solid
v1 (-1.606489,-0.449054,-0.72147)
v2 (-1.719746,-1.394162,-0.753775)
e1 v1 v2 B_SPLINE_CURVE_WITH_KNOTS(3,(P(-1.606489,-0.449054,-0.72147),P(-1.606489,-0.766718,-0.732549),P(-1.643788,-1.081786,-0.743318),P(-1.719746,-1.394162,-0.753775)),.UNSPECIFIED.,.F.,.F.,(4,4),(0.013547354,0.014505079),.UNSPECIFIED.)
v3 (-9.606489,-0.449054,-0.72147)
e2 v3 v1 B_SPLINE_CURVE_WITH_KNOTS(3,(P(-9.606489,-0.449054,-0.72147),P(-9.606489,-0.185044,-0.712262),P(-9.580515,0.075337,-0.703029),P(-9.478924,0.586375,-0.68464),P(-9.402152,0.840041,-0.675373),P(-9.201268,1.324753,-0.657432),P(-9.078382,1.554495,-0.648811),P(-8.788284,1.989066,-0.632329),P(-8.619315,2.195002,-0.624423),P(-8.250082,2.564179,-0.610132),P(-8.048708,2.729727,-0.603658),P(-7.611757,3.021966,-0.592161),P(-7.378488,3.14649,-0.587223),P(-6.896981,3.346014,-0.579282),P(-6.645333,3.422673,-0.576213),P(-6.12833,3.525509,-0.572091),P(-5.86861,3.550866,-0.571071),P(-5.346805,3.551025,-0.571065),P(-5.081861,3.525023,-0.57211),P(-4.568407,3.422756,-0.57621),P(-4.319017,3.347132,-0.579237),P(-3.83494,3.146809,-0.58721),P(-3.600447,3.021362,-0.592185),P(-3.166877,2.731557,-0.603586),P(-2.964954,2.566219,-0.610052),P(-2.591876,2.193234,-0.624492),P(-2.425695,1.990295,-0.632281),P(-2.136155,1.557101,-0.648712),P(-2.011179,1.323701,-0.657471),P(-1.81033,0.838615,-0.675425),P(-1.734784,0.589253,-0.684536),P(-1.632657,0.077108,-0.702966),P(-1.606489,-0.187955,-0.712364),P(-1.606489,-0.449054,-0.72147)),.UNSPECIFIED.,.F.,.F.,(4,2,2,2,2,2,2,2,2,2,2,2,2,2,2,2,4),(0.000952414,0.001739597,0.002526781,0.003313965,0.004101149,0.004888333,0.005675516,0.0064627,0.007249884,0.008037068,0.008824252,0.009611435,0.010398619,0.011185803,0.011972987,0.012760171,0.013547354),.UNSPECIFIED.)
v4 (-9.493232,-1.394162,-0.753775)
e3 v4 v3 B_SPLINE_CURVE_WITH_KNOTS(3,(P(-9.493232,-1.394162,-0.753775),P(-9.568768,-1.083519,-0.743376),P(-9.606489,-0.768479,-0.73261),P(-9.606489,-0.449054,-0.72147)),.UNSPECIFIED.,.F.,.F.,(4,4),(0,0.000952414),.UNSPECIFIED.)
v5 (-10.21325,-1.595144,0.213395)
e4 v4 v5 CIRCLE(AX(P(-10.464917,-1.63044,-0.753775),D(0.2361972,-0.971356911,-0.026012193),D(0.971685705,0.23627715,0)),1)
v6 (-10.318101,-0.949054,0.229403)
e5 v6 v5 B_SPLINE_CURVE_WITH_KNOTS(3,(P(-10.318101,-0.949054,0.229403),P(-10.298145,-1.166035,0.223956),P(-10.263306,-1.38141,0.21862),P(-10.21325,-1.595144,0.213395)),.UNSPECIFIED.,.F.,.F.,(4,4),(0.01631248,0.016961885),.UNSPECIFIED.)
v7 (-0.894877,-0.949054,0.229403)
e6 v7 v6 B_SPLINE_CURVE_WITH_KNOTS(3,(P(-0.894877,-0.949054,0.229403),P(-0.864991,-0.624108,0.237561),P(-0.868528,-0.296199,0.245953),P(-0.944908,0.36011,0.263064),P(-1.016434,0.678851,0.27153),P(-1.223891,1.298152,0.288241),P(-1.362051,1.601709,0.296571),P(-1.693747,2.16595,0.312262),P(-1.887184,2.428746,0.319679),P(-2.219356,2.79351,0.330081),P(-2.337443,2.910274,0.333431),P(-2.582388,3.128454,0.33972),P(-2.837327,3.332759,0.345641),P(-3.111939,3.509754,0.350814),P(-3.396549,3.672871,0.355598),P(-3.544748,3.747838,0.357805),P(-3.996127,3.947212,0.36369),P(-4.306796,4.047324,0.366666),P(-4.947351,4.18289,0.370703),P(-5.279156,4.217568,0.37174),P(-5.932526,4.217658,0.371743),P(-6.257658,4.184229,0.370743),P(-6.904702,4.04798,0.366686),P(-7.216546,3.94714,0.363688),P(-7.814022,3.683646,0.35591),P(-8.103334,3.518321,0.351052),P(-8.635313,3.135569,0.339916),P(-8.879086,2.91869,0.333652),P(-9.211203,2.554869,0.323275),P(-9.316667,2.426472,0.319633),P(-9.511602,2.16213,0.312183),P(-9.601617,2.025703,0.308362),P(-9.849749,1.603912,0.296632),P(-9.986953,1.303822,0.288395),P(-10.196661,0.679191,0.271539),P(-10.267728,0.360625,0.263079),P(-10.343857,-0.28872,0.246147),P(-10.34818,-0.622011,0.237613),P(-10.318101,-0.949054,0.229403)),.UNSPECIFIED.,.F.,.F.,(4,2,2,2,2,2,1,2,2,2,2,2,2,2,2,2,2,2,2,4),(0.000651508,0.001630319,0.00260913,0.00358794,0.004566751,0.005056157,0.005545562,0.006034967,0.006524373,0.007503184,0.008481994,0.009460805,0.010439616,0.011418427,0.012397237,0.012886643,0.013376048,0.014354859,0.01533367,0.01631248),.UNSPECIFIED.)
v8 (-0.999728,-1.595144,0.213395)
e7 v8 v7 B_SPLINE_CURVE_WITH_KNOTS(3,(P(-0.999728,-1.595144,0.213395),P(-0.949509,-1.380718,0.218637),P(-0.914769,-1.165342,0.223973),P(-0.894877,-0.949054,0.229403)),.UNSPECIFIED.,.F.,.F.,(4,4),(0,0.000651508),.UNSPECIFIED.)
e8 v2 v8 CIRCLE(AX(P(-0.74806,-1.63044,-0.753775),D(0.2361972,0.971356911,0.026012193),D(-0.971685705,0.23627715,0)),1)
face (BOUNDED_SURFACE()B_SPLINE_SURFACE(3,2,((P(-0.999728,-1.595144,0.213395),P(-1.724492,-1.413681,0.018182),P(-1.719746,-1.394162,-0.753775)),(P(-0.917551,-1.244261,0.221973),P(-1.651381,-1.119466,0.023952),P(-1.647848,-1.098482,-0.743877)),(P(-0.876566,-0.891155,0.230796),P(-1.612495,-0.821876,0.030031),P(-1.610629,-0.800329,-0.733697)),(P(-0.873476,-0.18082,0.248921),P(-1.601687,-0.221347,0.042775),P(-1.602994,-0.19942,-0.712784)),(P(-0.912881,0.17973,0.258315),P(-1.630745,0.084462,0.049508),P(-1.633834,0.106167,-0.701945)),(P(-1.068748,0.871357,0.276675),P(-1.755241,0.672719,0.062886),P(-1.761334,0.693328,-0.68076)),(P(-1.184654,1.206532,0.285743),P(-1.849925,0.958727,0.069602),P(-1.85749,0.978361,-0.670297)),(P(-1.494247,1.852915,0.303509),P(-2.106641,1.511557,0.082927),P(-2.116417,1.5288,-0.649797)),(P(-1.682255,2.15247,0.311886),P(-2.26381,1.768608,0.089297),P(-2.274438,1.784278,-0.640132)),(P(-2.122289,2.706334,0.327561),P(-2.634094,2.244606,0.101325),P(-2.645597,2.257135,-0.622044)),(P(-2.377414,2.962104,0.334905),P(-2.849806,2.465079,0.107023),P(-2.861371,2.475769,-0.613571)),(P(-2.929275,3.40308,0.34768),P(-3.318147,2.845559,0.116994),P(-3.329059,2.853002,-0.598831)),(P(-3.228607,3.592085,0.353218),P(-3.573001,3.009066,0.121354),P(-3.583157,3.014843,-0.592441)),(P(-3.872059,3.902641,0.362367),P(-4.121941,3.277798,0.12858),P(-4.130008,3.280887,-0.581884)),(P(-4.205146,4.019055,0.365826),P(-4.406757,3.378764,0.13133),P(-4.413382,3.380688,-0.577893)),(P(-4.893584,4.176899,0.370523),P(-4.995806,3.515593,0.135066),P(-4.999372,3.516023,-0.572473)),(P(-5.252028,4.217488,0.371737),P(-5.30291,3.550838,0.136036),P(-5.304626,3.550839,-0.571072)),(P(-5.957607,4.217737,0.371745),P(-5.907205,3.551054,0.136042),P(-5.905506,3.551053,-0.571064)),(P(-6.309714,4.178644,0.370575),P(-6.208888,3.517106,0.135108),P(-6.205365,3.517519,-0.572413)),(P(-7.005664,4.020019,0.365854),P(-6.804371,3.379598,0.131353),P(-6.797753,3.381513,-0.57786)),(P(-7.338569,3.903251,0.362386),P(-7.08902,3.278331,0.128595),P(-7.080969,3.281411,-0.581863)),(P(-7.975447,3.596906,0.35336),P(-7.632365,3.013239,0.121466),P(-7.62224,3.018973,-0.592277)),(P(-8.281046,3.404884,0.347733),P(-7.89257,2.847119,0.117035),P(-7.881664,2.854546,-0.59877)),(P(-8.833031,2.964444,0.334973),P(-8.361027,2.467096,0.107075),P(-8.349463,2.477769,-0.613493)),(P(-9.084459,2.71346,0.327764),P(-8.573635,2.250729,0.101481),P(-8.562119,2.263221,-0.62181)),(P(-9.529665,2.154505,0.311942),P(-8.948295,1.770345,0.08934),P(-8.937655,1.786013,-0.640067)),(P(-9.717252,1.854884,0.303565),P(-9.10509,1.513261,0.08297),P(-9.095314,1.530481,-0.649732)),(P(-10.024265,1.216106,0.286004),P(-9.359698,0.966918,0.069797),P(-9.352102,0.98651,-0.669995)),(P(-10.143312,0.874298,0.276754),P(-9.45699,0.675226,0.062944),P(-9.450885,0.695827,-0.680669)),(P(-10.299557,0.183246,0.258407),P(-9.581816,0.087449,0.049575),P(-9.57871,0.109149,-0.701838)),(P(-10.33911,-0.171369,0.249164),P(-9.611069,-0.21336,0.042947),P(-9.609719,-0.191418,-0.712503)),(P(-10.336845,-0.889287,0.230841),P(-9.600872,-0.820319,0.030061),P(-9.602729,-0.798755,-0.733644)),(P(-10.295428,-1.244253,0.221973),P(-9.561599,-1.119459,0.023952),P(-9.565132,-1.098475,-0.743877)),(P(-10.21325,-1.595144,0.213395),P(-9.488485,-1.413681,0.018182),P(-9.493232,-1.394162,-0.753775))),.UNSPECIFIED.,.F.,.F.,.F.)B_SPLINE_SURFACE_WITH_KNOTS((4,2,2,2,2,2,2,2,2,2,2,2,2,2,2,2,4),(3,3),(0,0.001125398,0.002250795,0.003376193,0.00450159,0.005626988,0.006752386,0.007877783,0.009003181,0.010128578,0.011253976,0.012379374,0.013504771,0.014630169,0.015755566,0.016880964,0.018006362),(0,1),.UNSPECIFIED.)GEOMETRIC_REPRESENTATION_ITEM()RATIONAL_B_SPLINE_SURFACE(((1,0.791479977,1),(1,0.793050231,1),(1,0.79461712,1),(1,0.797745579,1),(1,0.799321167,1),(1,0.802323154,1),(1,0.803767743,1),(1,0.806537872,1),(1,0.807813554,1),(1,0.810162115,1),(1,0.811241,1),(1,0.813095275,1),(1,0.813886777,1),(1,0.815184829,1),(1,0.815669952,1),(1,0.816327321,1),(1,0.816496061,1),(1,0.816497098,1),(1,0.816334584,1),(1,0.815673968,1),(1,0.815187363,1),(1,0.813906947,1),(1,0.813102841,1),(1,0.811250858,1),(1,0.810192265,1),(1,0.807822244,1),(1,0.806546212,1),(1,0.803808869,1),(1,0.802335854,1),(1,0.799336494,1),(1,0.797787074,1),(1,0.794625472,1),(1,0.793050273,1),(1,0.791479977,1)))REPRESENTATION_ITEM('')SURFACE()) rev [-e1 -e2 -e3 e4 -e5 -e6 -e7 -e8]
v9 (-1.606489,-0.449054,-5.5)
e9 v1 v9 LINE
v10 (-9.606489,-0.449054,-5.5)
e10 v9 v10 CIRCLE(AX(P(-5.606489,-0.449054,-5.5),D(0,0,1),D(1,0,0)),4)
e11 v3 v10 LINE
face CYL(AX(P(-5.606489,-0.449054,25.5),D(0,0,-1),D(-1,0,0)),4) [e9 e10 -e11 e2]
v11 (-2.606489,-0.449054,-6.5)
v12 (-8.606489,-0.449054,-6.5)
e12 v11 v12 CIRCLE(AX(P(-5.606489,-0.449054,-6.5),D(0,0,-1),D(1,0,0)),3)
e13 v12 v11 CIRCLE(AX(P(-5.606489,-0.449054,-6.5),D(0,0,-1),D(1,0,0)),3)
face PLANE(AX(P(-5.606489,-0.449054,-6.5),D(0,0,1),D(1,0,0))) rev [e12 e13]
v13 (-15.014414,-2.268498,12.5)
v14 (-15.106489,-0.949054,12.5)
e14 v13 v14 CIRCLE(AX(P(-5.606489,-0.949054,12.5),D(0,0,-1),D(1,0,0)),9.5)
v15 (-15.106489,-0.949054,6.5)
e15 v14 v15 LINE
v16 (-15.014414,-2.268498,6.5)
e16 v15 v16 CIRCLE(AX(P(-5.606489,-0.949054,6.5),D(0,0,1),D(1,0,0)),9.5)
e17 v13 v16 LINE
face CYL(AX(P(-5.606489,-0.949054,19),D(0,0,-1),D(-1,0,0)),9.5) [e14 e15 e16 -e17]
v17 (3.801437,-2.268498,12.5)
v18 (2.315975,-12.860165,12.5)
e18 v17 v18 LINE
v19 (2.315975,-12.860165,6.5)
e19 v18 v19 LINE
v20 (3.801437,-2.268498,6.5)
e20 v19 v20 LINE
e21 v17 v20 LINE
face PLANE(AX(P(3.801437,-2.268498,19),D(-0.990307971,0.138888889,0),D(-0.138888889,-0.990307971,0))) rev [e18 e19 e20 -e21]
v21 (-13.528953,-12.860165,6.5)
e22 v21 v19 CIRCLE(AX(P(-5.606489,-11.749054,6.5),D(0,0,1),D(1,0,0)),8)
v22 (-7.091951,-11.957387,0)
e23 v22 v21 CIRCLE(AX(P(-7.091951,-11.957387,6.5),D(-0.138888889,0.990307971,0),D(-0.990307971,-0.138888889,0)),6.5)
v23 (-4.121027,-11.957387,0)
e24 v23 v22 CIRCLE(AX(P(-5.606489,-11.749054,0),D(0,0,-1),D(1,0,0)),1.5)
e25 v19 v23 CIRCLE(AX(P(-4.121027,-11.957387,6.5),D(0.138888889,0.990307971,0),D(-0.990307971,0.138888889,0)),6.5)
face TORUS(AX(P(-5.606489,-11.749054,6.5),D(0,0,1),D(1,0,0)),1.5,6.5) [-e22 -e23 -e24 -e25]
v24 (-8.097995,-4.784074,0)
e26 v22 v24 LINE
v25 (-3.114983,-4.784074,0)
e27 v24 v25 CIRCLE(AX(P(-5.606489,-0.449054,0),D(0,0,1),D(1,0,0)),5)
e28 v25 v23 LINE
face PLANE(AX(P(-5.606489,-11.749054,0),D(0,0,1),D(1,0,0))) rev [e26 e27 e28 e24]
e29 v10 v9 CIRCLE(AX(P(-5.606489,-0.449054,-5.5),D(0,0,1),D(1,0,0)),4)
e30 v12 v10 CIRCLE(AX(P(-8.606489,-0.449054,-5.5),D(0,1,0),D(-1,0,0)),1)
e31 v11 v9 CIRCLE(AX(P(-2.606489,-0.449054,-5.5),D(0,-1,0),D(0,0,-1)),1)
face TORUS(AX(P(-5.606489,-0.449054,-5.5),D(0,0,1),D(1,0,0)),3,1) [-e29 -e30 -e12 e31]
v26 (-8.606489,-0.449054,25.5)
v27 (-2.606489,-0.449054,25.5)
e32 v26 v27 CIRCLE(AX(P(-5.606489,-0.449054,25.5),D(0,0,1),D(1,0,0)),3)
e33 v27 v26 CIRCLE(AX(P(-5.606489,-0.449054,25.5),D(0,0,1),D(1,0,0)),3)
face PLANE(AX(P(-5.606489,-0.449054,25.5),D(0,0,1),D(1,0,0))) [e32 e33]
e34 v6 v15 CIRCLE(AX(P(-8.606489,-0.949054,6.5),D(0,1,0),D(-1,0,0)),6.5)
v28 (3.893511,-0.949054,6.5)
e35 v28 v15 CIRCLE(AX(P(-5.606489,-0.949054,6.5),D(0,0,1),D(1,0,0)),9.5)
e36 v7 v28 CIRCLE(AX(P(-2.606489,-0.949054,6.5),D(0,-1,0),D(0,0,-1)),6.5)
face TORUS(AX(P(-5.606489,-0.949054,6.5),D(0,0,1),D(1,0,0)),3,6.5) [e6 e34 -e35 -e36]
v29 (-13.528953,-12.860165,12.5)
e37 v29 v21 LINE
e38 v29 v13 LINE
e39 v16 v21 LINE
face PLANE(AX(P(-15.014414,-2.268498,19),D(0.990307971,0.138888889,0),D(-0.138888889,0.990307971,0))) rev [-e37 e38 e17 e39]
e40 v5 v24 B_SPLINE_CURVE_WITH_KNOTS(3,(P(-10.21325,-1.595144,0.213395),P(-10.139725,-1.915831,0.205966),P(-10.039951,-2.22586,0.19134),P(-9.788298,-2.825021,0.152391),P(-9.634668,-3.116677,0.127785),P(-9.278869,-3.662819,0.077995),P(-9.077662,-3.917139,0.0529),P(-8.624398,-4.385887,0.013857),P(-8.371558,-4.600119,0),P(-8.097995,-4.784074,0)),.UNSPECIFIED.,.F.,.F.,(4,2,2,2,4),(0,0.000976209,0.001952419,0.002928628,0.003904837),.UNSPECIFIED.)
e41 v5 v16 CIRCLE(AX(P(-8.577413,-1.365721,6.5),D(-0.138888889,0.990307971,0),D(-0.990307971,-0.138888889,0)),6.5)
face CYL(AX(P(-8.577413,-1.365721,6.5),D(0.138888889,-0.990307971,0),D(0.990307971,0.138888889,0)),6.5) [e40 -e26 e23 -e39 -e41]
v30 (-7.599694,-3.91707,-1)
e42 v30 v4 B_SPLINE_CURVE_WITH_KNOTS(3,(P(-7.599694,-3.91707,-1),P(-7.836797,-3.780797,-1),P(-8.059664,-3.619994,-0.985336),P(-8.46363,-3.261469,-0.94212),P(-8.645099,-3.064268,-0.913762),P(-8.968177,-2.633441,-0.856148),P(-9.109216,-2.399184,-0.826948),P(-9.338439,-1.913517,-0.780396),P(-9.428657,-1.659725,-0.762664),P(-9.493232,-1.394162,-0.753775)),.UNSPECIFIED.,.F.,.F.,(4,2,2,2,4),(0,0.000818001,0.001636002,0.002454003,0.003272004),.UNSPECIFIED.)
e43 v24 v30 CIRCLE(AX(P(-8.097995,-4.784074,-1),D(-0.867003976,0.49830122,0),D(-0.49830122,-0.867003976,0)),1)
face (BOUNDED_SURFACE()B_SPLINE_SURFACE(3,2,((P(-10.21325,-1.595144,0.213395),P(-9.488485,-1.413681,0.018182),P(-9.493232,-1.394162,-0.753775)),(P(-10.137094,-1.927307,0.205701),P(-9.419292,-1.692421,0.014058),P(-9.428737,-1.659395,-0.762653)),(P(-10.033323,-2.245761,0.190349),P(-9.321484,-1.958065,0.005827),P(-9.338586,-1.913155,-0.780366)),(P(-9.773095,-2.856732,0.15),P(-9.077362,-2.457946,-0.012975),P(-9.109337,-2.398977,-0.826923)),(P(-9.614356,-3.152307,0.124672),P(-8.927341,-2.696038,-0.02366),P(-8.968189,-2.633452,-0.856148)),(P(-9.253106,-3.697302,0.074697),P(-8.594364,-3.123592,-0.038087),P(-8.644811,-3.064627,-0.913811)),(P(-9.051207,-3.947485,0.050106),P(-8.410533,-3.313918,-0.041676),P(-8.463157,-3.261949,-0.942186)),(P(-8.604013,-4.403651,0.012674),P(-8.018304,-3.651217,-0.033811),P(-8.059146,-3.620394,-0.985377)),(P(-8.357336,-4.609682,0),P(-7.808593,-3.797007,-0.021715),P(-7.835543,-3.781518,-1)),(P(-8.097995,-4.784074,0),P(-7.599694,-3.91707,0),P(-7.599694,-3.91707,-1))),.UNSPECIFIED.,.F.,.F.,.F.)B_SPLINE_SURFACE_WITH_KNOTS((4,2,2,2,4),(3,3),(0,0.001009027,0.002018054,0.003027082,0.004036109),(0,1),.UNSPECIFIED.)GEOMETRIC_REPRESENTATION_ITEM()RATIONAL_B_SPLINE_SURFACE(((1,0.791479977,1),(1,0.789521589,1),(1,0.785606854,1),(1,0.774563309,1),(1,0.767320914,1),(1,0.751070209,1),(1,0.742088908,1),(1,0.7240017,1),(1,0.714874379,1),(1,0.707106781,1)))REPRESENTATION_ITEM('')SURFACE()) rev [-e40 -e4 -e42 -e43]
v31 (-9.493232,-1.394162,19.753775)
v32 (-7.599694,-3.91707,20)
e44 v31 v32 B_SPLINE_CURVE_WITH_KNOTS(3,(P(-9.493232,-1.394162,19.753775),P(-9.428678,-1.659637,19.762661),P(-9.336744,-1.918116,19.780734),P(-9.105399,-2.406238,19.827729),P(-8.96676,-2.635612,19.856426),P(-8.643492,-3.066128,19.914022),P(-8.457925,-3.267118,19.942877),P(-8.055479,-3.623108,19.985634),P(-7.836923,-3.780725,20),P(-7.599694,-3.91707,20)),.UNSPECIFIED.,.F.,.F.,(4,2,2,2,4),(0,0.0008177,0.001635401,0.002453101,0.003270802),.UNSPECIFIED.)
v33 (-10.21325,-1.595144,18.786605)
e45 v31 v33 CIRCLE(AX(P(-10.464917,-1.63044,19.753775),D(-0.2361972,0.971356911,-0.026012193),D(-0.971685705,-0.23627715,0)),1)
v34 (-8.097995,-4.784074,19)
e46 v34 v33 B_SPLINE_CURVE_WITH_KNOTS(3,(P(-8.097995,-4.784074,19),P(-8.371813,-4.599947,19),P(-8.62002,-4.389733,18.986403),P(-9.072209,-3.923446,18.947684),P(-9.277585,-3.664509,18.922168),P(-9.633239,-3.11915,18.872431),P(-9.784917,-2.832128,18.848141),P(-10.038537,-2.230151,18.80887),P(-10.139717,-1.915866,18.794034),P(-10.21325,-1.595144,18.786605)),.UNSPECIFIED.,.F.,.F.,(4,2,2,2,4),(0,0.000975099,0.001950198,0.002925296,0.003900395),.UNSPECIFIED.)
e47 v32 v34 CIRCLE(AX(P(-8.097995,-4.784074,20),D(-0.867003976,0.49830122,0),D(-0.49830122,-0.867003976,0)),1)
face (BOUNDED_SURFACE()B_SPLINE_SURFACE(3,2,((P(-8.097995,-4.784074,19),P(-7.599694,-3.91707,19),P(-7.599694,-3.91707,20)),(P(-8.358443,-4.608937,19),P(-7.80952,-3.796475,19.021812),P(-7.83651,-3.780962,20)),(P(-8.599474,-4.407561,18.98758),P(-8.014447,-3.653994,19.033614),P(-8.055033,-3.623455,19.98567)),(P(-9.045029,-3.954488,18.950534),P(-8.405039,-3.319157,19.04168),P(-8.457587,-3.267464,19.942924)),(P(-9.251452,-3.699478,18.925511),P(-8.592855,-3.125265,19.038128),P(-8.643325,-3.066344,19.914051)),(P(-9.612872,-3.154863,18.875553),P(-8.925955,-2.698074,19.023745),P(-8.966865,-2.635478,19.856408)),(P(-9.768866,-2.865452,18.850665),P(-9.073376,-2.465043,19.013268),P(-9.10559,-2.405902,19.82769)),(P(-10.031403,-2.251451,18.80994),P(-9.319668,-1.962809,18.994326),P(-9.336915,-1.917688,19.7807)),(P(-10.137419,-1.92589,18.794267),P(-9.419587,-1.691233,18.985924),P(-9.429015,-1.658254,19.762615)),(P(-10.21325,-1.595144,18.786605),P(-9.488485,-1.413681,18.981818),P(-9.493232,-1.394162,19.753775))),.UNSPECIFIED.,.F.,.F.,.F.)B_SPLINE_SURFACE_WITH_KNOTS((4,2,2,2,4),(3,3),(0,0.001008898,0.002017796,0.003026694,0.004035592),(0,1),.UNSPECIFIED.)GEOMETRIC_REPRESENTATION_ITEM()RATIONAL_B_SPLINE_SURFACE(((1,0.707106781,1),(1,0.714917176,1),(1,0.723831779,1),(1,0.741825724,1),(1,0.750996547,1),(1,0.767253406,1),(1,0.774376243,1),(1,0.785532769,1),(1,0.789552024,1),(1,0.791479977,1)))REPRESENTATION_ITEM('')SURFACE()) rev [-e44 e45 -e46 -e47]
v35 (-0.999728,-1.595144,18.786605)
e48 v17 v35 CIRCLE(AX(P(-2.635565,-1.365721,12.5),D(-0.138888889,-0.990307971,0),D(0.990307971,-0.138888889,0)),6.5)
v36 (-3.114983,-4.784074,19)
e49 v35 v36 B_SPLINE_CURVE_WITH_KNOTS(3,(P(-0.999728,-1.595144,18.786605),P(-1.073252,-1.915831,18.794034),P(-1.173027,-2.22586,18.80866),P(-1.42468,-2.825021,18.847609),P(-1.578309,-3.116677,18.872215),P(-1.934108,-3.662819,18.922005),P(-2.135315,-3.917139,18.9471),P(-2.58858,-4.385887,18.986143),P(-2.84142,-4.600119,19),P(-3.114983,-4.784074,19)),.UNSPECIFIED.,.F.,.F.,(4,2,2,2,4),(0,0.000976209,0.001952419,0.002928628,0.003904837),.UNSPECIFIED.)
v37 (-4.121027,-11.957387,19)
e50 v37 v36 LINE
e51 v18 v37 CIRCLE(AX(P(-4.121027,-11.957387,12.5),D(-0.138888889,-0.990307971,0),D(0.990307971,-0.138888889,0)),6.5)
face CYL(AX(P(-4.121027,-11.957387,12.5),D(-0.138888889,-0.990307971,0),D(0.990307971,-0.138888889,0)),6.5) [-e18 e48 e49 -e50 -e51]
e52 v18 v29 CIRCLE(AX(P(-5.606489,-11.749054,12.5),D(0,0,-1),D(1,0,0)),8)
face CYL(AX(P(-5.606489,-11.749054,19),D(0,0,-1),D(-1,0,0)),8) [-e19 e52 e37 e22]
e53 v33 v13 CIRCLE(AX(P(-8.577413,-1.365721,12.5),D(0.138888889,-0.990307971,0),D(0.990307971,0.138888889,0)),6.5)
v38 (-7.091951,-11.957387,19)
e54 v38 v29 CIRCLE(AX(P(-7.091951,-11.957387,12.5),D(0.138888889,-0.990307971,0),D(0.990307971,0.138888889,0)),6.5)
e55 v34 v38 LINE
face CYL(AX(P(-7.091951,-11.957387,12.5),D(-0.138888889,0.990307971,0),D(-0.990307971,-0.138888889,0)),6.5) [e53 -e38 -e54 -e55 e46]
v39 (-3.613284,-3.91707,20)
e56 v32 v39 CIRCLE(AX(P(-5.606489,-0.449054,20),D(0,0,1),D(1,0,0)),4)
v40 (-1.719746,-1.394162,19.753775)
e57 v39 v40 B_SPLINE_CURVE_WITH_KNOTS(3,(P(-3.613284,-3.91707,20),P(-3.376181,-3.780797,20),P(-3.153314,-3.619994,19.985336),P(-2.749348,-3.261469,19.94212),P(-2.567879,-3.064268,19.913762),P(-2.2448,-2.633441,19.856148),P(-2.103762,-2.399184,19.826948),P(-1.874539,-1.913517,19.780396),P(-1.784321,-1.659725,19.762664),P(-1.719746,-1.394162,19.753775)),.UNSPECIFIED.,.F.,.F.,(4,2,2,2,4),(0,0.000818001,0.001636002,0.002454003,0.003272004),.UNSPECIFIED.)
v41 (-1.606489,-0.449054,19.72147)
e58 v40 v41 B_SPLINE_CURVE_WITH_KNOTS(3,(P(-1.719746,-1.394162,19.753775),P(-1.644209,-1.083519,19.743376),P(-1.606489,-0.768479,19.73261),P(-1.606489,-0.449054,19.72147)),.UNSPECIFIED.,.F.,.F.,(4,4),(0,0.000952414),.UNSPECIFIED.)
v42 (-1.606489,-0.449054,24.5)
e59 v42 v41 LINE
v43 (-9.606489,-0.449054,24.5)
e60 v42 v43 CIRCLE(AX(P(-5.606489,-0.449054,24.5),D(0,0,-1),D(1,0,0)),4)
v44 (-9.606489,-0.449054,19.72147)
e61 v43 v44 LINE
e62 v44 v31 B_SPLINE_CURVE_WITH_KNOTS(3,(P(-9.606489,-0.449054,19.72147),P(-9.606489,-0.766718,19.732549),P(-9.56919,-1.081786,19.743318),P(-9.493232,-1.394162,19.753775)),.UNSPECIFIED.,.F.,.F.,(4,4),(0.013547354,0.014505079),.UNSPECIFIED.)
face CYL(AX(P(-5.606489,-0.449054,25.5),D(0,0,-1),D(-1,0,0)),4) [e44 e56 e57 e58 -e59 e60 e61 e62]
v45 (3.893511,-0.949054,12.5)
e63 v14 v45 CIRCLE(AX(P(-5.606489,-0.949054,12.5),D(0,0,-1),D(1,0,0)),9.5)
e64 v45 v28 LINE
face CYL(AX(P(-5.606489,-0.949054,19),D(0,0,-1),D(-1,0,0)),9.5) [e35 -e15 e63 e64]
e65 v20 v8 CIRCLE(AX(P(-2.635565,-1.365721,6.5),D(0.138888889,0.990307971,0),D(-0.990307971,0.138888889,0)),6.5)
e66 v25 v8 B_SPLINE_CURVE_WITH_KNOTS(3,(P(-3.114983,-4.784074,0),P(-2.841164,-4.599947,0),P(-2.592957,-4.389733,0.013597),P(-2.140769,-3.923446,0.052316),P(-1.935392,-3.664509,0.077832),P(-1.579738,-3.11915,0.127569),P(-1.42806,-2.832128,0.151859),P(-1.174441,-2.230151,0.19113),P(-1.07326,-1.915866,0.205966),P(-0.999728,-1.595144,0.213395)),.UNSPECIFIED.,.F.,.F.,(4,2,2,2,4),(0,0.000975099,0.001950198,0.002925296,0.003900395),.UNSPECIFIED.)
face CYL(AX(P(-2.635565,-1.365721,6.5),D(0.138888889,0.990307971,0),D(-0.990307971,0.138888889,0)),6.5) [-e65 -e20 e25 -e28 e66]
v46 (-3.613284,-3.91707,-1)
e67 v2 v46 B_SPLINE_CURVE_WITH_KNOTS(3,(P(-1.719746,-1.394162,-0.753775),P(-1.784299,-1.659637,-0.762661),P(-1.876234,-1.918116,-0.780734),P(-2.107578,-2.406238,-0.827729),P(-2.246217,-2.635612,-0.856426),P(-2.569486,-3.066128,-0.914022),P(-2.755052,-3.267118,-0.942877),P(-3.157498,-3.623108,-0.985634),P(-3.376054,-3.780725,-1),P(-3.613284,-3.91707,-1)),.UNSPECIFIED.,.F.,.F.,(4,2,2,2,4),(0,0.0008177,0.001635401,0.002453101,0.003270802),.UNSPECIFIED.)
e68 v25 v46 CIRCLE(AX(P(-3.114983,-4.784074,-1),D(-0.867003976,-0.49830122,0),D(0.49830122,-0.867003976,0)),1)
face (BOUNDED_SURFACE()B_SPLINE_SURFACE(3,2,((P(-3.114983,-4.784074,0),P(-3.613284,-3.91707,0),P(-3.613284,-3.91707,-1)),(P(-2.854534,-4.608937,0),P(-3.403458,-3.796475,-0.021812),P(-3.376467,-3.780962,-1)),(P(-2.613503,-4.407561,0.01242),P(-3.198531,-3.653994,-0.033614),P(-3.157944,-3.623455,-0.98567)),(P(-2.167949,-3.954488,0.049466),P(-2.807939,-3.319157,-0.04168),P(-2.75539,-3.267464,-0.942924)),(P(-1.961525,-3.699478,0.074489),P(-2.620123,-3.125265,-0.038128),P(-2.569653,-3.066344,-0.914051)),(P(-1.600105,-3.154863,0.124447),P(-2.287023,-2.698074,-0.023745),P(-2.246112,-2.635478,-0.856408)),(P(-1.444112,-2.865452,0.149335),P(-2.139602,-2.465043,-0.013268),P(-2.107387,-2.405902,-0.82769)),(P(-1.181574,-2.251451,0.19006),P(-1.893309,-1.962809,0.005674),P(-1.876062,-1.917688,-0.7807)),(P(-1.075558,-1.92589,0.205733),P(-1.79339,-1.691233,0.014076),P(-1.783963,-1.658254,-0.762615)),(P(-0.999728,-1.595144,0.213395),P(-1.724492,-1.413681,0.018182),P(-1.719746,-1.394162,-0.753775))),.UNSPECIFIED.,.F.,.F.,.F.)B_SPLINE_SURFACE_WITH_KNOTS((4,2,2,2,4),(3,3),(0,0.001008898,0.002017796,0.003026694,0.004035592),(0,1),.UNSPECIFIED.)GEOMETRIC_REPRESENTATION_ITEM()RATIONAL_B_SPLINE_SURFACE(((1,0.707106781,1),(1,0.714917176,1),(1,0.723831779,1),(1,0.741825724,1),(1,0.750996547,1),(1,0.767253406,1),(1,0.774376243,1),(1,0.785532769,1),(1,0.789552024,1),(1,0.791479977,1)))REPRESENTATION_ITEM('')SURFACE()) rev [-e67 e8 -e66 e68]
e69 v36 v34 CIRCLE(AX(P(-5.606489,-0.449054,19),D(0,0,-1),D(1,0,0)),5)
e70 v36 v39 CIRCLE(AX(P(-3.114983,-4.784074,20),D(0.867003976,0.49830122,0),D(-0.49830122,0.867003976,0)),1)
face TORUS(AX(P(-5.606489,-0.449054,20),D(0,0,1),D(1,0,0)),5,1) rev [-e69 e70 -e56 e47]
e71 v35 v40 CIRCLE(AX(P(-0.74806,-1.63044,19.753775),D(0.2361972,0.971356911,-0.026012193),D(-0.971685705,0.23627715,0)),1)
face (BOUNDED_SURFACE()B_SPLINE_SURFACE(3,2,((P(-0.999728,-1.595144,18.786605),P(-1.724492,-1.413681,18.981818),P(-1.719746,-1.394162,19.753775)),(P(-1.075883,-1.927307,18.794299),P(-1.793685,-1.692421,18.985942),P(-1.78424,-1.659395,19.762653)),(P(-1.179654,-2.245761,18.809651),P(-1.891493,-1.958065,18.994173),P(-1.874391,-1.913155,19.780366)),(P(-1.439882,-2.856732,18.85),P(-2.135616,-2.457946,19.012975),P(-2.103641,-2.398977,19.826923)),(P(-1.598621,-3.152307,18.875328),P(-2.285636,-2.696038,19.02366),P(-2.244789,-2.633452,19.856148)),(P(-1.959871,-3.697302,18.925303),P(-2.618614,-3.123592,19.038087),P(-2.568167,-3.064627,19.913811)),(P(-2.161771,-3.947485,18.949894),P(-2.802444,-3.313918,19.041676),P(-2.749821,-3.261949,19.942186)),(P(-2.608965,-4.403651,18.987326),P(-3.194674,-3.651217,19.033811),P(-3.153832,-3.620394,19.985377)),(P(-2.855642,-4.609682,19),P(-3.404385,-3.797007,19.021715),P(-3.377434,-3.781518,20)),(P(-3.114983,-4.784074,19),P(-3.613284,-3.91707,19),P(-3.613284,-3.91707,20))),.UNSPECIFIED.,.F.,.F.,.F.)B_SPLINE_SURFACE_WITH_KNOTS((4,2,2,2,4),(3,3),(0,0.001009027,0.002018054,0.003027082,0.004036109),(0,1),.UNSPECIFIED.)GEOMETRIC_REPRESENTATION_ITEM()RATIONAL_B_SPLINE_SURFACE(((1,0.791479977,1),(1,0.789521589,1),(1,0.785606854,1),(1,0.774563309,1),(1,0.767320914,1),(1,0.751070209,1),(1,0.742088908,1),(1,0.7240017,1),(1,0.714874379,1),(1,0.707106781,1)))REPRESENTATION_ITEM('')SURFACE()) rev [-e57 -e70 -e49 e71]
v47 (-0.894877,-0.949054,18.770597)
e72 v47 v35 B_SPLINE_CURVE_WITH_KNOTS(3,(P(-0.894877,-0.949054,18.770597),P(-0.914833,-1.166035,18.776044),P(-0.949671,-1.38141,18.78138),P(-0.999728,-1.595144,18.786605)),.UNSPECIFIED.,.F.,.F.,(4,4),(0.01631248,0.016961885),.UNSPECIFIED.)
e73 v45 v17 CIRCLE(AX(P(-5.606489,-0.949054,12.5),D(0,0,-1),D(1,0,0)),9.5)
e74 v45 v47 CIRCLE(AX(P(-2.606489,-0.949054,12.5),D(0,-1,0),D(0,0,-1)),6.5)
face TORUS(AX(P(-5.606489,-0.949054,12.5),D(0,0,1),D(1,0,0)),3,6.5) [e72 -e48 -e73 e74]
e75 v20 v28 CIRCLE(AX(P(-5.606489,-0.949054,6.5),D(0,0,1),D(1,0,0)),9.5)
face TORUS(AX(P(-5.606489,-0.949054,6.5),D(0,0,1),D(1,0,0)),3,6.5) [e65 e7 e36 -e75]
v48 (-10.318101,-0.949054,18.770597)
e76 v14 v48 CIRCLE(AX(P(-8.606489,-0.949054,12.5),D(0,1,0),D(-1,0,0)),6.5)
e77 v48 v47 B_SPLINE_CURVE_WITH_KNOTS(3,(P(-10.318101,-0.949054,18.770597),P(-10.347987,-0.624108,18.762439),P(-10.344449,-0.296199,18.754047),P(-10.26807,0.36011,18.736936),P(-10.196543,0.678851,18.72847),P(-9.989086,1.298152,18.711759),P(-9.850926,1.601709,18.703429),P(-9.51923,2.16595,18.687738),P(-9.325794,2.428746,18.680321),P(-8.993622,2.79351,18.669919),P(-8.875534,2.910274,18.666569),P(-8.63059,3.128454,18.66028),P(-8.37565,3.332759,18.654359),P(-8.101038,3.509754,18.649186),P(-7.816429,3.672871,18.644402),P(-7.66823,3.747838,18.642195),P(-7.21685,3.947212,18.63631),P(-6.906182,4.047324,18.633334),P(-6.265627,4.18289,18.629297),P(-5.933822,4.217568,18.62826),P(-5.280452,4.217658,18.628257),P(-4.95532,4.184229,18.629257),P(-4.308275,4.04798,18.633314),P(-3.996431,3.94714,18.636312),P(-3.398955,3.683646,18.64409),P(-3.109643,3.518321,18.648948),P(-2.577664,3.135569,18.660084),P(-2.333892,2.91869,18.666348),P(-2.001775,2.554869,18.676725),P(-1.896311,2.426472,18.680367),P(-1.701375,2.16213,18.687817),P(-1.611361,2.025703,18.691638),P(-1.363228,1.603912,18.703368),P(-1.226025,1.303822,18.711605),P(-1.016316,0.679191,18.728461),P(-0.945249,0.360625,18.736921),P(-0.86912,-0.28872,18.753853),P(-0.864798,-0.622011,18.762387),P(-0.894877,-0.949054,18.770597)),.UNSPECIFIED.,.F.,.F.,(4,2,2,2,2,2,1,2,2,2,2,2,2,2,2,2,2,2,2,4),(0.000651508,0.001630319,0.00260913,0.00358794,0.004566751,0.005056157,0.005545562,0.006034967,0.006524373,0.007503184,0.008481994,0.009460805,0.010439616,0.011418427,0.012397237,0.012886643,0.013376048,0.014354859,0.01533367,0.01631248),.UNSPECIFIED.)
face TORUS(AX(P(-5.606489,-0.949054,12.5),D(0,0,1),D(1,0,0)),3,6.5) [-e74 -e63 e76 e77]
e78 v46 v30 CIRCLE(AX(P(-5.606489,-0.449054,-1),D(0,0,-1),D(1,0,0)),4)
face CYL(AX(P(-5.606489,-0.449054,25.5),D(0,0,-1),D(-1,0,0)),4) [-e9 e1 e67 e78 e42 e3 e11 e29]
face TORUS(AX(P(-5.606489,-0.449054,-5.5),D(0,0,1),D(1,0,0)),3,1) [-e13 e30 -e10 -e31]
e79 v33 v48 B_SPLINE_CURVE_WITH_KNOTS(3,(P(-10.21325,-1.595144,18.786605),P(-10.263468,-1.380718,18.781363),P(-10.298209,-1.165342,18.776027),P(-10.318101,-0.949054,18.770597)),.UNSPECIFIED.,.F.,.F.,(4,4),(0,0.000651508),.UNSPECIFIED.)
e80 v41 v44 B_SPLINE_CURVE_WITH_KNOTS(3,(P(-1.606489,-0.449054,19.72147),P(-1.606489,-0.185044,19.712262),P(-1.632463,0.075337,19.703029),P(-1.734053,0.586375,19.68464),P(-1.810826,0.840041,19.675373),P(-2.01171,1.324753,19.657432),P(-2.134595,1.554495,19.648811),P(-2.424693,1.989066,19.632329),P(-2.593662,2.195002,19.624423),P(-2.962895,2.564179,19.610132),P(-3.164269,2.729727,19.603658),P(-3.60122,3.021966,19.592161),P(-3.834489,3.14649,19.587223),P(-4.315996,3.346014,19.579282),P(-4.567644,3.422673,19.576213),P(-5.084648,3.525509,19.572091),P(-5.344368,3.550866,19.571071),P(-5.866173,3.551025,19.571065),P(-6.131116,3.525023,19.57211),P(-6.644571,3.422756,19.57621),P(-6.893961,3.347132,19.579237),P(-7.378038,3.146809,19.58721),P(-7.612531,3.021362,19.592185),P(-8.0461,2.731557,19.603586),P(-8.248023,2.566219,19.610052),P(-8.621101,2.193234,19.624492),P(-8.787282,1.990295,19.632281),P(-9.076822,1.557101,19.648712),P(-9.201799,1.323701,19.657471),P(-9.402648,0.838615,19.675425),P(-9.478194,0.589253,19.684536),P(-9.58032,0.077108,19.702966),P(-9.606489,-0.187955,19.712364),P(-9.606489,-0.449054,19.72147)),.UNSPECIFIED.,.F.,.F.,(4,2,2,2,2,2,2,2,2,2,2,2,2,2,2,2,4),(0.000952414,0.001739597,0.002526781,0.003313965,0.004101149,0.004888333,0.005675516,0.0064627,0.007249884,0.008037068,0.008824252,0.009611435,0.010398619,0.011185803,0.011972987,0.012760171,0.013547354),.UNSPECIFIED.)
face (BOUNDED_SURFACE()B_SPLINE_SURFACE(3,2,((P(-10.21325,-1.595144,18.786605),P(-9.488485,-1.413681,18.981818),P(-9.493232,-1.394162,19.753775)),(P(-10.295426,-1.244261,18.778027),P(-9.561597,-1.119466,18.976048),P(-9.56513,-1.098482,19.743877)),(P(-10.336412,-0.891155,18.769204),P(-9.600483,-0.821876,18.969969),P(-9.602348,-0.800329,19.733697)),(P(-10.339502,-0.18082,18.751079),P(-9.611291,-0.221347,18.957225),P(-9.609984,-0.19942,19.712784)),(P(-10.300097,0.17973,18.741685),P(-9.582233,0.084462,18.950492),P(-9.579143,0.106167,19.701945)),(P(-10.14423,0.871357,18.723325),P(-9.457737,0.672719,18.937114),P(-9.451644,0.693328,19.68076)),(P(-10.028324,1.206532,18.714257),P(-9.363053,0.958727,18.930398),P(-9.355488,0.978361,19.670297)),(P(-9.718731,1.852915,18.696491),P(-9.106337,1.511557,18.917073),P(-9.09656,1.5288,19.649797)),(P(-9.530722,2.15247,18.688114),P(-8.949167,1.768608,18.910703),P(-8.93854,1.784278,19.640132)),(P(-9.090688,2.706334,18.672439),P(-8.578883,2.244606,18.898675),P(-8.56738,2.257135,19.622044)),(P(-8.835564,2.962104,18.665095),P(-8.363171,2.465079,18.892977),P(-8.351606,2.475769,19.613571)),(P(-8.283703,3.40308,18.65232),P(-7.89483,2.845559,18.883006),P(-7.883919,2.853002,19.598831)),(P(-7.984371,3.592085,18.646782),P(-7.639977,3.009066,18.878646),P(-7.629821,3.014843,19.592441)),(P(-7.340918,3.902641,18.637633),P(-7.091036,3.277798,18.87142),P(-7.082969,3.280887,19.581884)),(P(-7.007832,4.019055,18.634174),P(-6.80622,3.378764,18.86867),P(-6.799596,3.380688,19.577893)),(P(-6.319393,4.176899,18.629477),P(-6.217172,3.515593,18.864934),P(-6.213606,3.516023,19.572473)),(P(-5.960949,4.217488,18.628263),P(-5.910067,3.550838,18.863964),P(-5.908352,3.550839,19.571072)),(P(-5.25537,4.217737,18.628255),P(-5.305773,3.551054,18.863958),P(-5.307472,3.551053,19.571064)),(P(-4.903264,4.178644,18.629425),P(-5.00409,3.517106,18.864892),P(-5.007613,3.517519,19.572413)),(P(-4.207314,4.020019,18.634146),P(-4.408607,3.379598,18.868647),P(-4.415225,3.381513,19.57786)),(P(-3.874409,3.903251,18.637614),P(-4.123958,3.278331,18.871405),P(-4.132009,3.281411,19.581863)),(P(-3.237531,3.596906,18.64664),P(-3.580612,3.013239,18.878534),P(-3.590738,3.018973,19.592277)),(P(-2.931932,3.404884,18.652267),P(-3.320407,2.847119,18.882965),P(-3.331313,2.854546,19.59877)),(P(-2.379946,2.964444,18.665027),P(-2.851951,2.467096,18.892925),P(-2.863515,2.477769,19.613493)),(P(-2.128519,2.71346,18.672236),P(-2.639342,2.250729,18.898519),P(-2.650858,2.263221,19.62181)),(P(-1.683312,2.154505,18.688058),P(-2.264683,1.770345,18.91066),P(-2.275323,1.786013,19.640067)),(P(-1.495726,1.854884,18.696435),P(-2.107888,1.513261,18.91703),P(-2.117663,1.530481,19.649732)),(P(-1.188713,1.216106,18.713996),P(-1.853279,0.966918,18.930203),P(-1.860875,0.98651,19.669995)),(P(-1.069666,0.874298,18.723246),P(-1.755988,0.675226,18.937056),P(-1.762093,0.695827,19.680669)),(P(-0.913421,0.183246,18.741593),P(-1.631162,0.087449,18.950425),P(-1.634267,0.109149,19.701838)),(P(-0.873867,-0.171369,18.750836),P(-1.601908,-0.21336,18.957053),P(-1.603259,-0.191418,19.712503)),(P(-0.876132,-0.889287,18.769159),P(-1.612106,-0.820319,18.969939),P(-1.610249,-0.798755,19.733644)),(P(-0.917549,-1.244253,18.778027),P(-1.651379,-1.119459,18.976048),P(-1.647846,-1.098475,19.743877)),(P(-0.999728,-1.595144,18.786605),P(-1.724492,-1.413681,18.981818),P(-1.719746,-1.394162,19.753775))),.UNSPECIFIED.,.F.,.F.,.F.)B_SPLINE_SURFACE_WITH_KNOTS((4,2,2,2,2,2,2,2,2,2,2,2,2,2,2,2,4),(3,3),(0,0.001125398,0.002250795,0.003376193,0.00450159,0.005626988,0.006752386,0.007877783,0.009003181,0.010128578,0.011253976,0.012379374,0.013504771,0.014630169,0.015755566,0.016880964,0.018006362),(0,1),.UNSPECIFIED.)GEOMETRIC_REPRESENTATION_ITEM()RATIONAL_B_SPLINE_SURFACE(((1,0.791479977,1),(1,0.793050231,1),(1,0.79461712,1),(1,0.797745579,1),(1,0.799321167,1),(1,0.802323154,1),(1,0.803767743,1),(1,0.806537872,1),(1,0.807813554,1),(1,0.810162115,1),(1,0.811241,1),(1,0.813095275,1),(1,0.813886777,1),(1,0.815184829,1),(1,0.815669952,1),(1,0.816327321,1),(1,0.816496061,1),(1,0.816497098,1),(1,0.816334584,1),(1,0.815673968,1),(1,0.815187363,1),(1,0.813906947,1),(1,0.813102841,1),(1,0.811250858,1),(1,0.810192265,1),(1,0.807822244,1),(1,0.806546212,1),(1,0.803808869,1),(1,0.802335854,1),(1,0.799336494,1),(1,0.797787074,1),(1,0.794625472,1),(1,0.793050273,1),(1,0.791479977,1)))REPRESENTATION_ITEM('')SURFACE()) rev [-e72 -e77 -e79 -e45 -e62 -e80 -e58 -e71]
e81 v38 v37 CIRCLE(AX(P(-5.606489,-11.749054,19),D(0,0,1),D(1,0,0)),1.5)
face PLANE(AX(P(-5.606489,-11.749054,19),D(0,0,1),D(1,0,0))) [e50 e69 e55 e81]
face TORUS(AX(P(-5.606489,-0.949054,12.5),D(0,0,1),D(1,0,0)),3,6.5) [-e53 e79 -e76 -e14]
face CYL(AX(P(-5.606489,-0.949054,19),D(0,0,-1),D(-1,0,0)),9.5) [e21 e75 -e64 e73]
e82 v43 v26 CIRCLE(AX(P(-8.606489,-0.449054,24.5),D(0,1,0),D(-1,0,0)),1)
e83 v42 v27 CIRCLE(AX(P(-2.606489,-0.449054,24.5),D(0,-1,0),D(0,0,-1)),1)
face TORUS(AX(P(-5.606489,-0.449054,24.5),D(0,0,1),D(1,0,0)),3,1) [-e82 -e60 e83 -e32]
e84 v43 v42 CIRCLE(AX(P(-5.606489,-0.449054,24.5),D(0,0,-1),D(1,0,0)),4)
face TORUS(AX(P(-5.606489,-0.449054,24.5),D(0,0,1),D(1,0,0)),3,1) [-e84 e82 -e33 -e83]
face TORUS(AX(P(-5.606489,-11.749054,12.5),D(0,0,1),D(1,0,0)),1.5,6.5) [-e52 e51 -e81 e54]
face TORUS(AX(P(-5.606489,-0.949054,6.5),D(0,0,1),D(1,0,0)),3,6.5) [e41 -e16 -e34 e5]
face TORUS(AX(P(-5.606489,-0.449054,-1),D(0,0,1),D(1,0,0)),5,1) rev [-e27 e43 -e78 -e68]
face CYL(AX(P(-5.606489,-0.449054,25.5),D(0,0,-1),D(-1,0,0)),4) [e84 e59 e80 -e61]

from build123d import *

# Parameters (mm, degrees)
BOSS_EXTRUDE1_DEPTH = 19
FILLET1_R           = 6.5
SKETCH2_R           = 4
BOSS_EXTRUDE2_DEPTH = 16
FILLET2_R           = 1
FILLET4_R           = 1


with BuildPart() as part:
    # Sketch1 → Boss-Extrude1 (new body)
    with BuildSketch(Plane.XY):
        with BuildLine():
            Line((-15.01441447, -2.268498309), (-13.528952514, -12.860164976))
            ThreePointArc((-13.528952514, -12.860164976), (-5.606488749, -19.749053865), (2.315975015, -12.860164976))
            Line((2.315975015, -12.860164976), (3.801436971, -2.268498309))
            ThreePointArc((3.801436971, -2.268498309), (-5.606488749, 8.550946135), (-15.01441447, -2.268498309))
        make_face()
    extrude(amount=BOSS_EXTRUDE1_DEPTH)

    # Fillet1
    fillet1_edges = [part.edges().sort_by_distance(p)[0] for p in [
        (-5.606488749, 8.550946135, 19),
        (-14.271683492, -7.564331643, 19),
        (-5.606488749, -19.749053865, 19),
        (-14.271683492, -7.564331643, 0),
        (-5.606488749, 8.550946135, 0),
        (3.058705993, -7.564331643, 0),
        (-5.606488749, -19.749053865, 0),
        (3.058705993, -7.564331643, 19),
    ]]
    fillet(fillet1_edges, radius=FILLET1_R)

    # Sketch2 → Boss-Extrude2 (add, symmetric)
    with BuildSketch(Plane.XY.offset(9.5)):
        with Locations(Location((-5.606488749, -0.449053865, 0), (0, 0, 195.094354514))):
            Circle(SKETCH2_R)
    extrude(amount=BOSS_EXTRUDE2_DEPTH, both=True)

    # Fillet2
    fillet2_edges = [part.edges().sort_by_distance(p)[0] for p in [
        (-1.744495572, 0.592583644, -6.5),
        (-1.744495572, 0.592583644, 25.5),
    ]]
    fillet(fillet2_edges, radius=FILLET2_R)

    # Fillet4
    fillet4_edges = [part.edges().sort_by_distance(p)[0] for p in [
        (-2.195166372, -2.537804614, 18.972348526),
        (-5.606488749, -4.449053865, 0),
        (-2.195166372, -2.537804614, 0.027651474),
        (-5.606488749, 3.550946135, 0.17544468),
        (-9.017811127, -2.537804614, 0.027651474),
        (-5.606488749, -4.449053865, 19),
        (-9.017811127, -2.537804614, 18.972348526),
        (-5.606488749, 3.550946135, 18.82455532),
    ]]
    fillet(fillet4_edges, radius=FILLET4_R)


solid = part.part
